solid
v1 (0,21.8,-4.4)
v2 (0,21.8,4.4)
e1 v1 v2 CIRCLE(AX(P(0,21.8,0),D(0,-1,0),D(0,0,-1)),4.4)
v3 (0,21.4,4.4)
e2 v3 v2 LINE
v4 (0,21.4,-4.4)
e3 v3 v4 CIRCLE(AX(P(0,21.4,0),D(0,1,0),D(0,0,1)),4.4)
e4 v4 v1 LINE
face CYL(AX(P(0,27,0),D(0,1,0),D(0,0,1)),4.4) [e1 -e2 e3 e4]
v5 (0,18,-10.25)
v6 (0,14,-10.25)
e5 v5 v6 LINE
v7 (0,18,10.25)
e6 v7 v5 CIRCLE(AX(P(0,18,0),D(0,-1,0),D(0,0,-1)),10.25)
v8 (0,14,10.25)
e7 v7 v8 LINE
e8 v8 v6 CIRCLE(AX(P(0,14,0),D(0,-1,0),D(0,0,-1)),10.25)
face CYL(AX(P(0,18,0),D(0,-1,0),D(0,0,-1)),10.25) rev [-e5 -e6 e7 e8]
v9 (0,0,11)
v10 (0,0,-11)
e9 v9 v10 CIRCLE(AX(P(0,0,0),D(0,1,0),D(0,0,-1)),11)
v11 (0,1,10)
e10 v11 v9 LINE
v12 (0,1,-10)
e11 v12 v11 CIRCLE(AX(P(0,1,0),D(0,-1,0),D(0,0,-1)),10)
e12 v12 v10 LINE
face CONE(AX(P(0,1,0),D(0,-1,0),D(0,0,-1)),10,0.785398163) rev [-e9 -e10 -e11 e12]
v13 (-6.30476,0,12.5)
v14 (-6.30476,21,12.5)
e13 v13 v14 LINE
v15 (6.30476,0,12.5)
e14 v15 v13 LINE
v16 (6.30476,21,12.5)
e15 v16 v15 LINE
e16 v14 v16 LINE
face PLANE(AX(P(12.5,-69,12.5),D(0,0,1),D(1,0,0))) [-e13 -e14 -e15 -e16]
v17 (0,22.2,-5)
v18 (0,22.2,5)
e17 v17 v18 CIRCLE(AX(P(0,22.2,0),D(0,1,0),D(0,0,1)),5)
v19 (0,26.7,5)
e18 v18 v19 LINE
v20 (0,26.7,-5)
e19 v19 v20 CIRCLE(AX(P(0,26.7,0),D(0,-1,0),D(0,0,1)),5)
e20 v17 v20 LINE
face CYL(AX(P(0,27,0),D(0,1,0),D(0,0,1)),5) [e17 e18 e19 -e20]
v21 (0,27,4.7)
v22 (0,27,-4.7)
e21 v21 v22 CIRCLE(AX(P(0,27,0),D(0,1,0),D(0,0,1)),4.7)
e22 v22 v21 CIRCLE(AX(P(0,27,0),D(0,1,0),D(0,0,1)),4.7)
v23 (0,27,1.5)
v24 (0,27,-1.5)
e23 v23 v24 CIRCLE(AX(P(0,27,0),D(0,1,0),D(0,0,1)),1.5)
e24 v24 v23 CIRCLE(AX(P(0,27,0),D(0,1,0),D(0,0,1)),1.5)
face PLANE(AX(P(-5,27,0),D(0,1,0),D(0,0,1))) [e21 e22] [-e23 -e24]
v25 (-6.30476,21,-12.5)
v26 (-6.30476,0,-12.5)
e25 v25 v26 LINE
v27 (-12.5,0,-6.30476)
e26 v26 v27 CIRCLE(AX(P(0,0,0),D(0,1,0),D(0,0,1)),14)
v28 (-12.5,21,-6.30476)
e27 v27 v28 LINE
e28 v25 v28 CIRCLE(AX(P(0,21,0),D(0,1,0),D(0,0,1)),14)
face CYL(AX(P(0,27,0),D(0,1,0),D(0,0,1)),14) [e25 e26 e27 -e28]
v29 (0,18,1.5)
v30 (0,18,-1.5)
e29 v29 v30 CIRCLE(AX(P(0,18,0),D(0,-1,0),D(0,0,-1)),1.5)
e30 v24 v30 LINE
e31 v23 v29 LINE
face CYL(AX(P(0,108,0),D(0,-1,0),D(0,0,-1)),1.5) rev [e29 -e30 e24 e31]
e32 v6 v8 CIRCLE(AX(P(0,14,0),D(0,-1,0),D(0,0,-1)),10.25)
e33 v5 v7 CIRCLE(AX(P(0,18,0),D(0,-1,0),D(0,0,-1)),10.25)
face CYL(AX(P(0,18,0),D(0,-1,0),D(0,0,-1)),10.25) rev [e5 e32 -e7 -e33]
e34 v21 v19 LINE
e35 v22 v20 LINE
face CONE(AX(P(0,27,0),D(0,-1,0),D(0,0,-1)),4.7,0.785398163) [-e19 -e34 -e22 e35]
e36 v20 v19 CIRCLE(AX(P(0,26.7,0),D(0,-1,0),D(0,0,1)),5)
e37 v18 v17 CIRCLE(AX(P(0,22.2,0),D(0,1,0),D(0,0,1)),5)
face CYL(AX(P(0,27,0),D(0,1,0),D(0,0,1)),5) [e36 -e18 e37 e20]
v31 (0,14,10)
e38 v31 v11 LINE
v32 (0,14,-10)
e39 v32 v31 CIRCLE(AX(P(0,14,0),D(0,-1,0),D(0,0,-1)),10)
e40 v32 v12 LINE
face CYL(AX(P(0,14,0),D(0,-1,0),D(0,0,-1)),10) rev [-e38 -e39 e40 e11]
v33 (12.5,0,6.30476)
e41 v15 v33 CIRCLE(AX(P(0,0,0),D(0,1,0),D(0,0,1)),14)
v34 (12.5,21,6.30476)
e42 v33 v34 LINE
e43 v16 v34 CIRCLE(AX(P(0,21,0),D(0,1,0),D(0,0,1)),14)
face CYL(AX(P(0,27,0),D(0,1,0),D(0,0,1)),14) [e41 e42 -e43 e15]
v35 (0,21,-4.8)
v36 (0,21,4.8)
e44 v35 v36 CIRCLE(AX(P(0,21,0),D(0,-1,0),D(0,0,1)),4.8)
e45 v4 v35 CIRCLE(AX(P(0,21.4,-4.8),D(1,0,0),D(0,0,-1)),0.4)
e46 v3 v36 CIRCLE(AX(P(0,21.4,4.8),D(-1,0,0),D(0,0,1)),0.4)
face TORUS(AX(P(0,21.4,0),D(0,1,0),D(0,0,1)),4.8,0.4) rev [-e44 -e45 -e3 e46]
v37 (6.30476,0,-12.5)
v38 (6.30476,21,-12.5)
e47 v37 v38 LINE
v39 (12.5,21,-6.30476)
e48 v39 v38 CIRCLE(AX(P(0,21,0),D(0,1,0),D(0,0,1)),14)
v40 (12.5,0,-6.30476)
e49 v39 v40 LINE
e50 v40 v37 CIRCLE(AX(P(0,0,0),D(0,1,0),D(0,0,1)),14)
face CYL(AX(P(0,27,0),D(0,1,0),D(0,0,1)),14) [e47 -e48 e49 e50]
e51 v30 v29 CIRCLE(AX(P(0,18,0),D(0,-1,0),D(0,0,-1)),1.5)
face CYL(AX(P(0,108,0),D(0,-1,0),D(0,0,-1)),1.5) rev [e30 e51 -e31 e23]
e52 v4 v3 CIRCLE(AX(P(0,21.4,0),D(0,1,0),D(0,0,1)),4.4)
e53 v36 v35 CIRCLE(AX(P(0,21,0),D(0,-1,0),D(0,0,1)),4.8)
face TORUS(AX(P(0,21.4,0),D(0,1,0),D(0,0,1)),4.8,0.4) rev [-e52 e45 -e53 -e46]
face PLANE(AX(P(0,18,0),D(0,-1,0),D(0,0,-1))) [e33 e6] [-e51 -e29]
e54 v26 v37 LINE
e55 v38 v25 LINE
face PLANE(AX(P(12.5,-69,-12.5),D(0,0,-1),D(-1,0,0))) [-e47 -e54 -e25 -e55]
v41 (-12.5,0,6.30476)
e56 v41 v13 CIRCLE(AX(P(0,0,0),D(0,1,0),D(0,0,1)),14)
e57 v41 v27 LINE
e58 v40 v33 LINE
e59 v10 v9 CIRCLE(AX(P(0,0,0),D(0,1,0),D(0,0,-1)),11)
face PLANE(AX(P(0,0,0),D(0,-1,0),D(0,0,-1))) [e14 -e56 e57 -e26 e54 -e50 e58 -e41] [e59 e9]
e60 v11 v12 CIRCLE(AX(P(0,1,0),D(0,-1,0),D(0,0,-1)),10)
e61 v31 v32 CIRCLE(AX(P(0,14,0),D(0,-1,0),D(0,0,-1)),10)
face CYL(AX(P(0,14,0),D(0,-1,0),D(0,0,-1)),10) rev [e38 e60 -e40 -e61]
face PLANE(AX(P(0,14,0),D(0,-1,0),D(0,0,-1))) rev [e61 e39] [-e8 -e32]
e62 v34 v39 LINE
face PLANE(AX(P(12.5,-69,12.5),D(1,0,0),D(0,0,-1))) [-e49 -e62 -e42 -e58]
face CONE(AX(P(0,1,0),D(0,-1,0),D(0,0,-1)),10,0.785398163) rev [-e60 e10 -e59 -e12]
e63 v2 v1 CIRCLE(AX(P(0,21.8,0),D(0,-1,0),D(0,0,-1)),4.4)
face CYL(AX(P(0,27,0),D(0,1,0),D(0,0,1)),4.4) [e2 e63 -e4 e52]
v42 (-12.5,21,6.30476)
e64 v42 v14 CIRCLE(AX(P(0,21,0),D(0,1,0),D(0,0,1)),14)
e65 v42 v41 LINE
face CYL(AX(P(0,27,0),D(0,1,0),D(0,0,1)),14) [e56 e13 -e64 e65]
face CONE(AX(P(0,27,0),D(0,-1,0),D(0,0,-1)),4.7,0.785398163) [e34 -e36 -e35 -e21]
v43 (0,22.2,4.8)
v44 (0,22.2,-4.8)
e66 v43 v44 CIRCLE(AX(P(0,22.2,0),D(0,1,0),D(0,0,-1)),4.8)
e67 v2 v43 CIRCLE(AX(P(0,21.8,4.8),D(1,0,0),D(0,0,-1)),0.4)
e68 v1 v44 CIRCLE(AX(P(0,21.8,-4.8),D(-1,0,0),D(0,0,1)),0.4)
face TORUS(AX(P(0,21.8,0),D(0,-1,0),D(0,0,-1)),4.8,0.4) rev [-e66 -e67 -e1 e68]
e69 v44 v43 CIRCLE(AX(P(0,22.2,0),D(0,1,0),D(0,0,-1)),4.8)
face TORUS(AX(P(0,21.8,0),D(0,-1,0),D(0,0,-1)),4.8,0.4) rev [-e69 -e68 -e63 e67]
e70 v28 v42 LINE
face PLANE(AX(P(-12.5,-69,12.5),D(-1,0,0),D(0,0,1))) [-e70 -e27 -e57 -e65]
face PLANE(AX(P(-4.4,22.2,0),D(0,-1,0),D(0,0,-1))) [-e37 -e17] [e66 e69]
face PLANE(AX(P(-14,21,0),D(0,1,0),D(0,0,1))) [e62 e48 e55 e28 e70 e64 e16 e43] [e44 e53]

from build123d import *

# Parameters (mm, degrees)
FILLET1_R           = 0.4
SKETCH2_R           = 10
CUT_EXTRUDE1_DEPTH  = 14
SKETCH3_R           = 10.25
CUT_EXTRUDE2_DEPTH  = 4
SKETCH4_R           = 1.5
CUT_EXTRUDE3_DEPTH  = 90
CHAMFER1_SIZE       = 0.3
CHAMFER2_SIZE       = 1
SKETCH5_OUTSIDE_W   = 39.586
SKETCH5_OUTSIDE_H   = 39.586
SKETCH5_OUTSIDE_W_2 = 25
SKETCH5_OUTSIDE_H_2 = 25
CUT_EXTRUDE4_DEPTH  = 90


with BuildPart() as part:
    # Sketch1 → Revolve1 (revolve)
    with BuildSketch(Plane.XY, mode=Mode.PRIVATE) as revolve1_sk:
        Polygon((0, 0), (-14, 0), (-14, 21), (-4.4, 21), (-4.4, 22.2), (-5, 22.2), (-5, 27), (0, 27), align=None)
    revolve(revolve1_sk.sketch.rotate(Axis((0, 27, 0), (0, -1, 0)), 270), axis=Axis((0, 27, 0), (0, -1, 0)))

    # Fillet1
    fillet1_edges = [part.edges().sort_by_distance(p)[0] for p in [
        (0, 22.2, -4.4),
        (0, 21, -4.4),
    ]]
    fillet(fillet1_edges, radius=FILLET1_R)

    # Sketch2 → Cut-Extrude1 (cut)
    with BuildSketch(Plane.XZ):
        with Locations(Location((0, 0, 0), (0, 0, 270))):
            Circle(SKETCH2_R)
    extrude(amount=-CUT_EXTRUDE1_DEPTH, mode=Mode.SUBTRACT)

    # Sketch3 → Cut-Extrude2 (cut)
    with BuildSketch(Plane.XZ.offset(-14)):
        with Locations(Location((0, 0, 0), (0, 0, 270))):
            Circle(SKETCH3_R)
    extrude(amount=-CUT_EXTRUDE2_DEPTH, mode=Mode.SUBTRACT)

    # Sketch4 → Cut-Extrude3 (cut)
    with BuildSketch(Plane.XZ.offset(-18)):
        with Locations(Location((0, 0, 0), (0, 0, 270))):
            Circle(SKETCH4_R)
    extrude(amount=-CUT_EXTRUDE3_DEPTH, mode=Mode.SUBTRACT)

    # Chamfer1
    chamfer1_edges = [part.edges().sort_by_distance(p)[0] for p in [
        (0, 27, -5),
    ]]
    chamfer(chamfer1_edges, length=CHAMFER1_SIZE)

    # Chamfer2
    chamfer2_edges = [part.edges().sort_by_distance(p)[0] for p in [
        (0, 0, 10),
    ]]
    chamfer(chamfer2_edges, length=CHAMFER2_SIZE)

    # Sketch5 outside → Cut-Extrude4 (cut)
    with BuildSketch(Plane(origin=(0, 21, 0), x_dir=(1, 0, 0), z_dir=(0, 1, 0))):
        Rectangle(SKETCH5_OUTSIDE_W, SKETCH5_OUTSIDE_H)
        Rectangle(SKETCH5_OUTSIDE_W_2, SKETCH5_OUTSIDE_H_2, mode=Mode.SUBTRACT)
    extrude(amount=-CUT_EXTRUDE4_DEPTH, mode=Mode.SUBTRACT)


solid = part.part
